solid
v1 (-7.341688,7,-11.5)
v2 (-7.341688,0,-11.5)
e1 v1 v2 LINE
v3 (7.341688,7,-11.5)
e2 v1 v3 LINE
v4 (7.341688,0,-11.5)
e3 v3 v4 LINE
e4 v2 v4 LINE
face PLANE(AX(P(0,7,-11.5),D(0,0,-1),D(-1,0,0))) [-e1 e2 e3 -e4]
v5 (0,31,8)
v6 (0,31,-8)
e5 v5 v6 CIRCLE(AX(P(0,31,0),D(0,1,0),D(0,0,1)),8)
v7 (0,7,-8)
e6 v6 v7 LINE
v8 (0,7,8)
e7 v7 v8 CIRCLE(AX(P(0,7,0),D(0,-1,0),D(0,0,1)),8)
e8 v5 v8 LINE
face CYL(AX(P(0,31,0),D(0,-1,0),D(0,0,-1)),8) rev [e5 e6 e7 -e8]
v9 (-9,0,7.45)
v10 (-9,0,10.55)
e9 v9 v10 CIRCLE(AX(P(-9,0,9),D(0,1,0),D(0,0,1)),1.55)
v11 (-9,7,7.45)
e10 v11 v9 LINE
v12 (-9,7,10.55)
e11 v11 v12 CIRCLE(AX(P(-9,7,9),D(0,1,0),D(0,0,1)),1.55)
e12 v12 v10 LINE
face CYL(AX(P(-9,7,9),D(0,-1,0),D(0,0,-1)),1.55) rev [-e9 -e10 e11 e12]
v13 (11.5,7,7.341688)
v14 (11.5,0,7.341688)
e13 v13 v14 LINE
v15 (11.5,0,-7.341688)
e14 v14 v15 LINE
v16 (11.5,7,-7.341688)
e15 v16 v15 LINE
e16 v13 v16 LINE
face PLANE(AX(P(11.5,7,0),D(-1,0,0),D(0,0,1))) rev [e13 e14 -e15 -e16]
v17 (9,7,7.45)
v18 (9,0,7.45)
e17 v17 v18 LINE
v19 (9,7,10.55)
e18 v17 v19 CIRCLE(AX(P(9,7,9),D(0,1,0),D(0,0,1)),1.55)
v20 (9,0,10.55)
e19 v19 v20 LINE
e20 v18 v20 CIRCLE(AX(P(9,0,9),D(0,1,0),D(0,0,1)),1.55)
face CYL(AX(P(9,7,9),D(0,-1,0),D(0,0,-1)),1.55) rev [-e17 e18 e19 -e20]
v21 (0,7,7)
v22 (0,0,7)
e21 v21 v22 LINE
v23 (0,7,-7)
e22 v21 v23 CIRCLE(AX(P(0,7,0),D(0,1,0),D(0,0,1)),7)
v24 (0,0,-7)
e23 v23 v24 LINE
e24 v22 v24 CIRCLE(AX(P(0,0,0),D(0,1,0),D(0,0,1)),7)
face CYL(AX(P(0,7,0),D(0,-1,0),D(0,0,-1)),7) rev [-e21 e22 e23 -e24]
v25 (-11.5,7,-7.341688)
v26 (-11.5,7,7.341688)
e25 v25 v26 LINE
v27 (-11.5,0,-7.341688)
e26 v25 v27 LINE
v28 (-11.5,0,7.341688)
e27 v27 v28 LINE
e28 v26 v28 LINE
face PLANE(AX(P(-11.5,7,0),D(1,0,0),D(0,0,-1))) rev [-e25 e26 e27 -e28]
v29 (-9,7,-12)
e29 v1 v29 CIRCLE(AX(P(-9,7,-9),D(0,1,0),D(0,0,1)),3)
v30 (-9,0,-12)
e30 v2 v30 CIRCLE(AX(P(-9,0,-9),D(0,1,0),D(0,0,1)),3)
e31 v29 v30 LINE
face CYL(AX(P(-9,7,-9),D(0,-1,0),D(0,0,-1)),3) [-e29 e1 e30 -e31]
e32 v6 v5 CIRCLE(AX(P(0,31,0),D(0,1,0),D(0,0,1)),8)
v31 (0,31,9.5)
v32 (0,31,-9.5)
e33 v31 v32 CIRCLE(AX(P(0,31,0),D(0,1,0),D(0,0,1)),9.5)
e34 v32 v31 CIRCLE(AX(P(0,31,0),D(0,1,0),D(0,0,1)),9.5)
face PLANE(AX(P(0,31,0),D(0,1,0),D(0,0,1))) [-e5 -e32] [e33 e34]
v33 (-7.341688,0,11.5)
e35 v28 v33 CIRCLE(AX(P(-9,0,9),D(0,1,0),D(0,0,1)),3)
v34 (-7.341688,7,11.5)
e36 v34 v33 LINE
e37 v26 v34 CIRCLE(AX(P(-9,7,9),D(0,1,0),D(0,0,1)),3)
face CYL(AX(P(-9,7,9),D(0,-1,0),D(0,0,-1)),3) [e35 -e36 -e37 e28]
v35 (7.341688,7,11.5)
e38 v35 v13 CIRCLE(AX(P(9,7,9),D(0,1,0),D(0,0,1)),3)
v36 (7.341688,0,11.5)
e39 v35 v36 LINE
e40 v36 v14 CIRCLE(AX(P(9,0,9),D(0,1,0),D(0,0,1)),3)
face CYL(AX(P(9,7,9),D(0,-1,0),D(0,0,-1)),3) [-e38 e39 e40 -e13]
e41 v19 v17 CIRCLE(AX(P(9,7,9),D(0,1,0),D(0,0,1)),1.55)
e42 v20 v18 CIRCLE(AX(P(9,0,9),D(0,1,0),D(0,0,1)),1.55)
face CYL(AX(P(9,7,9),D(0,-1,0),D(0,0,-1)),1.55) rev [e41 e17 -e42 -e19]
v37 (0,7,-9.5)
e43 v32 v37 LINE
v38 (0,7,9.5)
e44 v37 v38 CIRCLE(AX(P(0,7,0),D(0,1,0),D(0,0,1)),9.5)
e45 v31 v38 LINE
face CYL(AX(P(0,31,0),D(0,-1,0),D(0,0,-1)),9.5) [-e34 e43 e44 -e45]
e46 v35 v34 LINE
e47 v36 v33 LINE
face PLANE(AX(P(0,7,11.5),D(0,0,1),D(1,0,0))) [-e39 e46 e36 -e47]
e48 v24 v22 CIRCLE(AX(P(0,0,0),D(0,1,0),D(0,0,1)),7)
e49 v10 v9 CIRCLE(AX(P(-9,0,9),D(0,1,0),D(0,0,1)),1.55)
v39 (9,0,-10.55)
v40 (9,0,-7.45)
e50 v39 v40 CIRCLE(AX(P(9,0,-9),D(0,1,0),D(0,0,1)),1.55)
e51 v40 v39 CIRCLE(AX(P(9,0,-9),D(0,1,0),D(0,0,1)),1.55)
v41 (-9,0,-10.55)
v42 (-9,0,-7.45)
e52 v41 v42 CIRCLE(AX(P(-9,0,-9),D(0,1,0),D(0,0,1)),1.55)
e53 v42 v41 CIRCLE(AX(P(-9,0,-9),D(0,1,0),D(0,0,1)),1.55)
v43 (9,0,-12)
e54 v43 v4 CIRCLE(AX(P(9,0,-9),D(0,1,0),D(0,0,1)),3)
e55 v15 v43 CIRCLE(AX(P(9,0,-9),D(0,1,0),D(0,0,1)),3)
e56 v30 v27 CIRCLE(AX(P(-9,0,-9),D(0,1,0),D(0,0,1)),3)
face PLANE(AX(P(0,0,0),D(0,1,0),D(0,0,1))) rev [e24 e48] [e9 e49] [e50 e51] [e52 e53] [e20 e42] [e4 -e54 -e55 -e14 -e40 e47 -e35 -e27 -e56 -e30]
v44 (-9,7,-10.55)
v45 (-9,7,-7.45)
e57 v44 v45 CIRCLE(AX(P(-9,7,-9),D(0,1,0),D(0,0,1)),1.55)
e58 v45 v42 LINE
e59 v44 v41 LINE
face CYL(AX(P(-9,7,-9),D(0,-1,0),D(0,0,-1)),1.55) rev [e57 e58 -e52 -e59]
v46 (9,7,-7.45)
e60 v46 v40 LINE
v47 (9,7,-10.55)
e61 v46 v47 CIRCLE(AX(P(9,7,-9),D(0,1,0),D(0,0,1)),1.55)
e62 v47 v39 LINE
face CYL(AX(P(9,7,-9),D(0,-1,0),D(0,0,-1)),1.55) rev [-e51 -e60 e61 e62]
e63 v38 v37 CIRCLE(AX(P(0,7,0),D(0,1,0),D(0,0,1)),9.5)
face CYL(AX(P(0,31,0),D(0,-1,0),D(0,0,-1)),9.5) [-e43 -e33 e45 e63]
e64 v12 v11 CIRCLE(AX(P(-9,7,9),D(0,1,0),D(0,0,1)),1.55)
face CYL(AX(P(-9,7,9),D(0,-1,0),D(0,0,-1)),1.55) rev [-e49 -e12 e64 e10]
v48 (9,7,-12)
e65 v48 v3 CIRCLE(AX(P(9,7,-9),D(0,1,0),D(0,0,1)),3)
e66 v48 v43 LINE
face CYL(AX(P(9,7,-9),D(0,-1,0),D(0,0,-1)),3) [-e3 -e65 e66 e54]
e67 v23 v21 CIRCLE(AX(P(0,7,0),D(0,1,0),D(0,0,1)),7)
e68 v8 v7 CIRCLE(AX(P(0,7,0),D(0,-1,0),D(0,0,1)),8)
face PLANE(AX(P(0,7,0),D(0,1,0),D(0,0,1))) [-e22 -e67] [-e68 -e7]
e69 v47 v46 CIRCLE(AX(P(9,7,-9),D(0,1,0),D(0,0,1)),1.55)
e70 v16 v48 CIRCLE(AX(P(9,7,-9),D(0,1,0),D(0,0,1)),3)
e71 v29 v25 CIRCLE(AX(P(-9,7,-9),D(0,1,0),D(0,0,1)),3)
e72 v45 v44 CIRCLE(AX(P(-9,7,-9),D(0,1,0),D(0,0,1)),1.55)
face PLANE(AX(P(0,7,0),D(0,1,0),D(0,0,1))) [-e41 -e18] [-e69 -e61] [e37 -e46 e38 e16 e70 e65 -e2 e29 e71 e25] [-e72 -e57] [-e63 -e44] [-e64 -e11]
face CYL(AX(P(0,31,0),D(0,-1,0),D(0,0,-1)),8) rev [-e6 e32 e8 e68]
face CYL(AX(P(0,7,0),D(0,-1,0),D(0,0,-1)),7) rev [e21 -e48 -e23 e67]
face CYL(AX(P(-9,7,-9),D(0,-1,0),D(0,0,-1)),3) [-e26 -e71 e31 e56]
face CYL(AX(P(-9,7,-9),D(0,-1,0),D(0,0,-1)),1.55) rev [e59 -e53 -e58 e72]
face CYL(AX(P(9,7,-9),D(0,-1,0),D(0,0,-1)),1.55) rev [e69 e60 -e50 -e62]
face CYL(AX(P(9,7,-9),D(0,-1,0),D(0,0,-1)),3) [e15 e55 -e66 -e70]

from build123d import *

# Parameters (mm, degrees)
SKETCH_1_R      = 7
SKETCH_1_R_2    = 3
SKETCH_1_R_3    = 1.55
EXTRUDE_1_DEPTH = 7
SKETCH_2_R      = 9.5
SKETCH_2_R_2    = 8
EXTRUDE_2_DEPTH = 24


with BuildPart() as part:
    # 草图1 → 凸台-拉伸1 (new body)
    # profile 1 of 5: a face of its own
    with BuildSketch(Plane(origin=(0, 0, 0), x_dir=(1, 0, 0), z_dir=(0, 1, 0))):
        with BuildLine():
            Line((7.341687605, 11.5), (-7.341687605, 11.5))
            ThreePointArc((-7.341687605, 11.5), (-6.356617963, 10.418637165), (-6, 9))
            ThreePointArc((-6, 9), (-8.133974596, 6.127718677), (-11.5, 7.341687605))
            Line((-11.5, 7.341687605), (-11.5, -7.341687605))
            ThreePointArc((-11.5, -7.341687605), (-8.133974596, -6.127718677), (-6, -9))
            ThreePointArc((-6, -9), (-6.356617963, -10.418637165), (-7.341687605, -11.5))
            Line((-7.341687605, -11.5), (7.341687605, -11.5))
            ThreePointArc((7.341687605, -11.5), (6.878679656, -6.878679656), (11.5, -7.341687605))
            Line((11.5, -7.341687605), (11.5, 7.341687605))
            ThreePointArc((11.5, 7.341687605), (6.878679656, 6.878679656), (7.341687605, 11.5))
        make_face()
        with Locations(Location((0, 0, 0), (0, 0, 270))):
            Circle(SKETCH_1_R, mode=Mode.SUBTRACT)
    # profile 2 of 5: a face of its own
    with BuildSketch(Plane(origin=(0, 0, 0), x_dir=(1, 0, 0), z_dir=(0, 1, 0))):
        with Locations((-9, -9)):
            Circle(SKETCH_1_R_2)
        with Locations(Location((-9, -9, 0), (0, 0, 270))):
            Circle(SKETCH_1_R_3, mode=Mode.SUBTRACT)
    # profile 3 of 5: a face of its own
    with BuildSketch(Plane(origin=(0, 0, 0), x_dir=(1, 0, 0), z_dir=(0, 1, 0))):
        with Locations((9, -9)):
            Circle(SKETCH_1_R_2)
        with Locations(Location((9, -9, 0), (0, 0, 270))):
            Circle(SKETCH_1_R_3, mode=Mode.SUBTRACT)
    # profile 4 of 5: a face of its own
    with BuildSketch(Plane(origin=(0, 0, 0), x_dir=(1, 0, 0), z_dir=(0, 1, 0))):
        with Locations((9, 9)):
            Circle(SKETCH_1_R_2)
        with Locations(Location((9, 9, 0), (0, 0, 270))):
            Circle(SKETCH_1_R_3, mode=Mode.SUBTRACT)
    # profile 5 of 5: a face of its own
    with BuildSketch(Plane(origin=(0, 0, 0), x_dir=(1, 0, 0), z_dir=(0, 1, 0))):
        with Locations((-9, 9)):
            Circle(SKETCH_1_R_2)
        with Locations(Location((-9, 9, 0), (0, 0, 270))):
            Circle(SKETCH_1_R_3, mode=Mode.SUBTRACT)
    extrude(amount=EXTRUDE_1_DEPTH)

    # 草图2 → 凸台-拉伸2 (add)
    with BuildSketch(Plane(origin=(0, 7, 0), x_dir=(1, 0, 0), z_dir=(0, 1, 0))):
        with Locations(Location((0, 0, 0), (0, 0, 270))):
            Circle(SKETCH_2_R)
        with Locations(Location((0, 0, 0), (0, 0, 270))):
            Circle(SKETCH_2_R_2, mode=Mode.SUBTRACT)
    extrude(amount=EXTRUDE_2_DEPTH)


solid = part.part
